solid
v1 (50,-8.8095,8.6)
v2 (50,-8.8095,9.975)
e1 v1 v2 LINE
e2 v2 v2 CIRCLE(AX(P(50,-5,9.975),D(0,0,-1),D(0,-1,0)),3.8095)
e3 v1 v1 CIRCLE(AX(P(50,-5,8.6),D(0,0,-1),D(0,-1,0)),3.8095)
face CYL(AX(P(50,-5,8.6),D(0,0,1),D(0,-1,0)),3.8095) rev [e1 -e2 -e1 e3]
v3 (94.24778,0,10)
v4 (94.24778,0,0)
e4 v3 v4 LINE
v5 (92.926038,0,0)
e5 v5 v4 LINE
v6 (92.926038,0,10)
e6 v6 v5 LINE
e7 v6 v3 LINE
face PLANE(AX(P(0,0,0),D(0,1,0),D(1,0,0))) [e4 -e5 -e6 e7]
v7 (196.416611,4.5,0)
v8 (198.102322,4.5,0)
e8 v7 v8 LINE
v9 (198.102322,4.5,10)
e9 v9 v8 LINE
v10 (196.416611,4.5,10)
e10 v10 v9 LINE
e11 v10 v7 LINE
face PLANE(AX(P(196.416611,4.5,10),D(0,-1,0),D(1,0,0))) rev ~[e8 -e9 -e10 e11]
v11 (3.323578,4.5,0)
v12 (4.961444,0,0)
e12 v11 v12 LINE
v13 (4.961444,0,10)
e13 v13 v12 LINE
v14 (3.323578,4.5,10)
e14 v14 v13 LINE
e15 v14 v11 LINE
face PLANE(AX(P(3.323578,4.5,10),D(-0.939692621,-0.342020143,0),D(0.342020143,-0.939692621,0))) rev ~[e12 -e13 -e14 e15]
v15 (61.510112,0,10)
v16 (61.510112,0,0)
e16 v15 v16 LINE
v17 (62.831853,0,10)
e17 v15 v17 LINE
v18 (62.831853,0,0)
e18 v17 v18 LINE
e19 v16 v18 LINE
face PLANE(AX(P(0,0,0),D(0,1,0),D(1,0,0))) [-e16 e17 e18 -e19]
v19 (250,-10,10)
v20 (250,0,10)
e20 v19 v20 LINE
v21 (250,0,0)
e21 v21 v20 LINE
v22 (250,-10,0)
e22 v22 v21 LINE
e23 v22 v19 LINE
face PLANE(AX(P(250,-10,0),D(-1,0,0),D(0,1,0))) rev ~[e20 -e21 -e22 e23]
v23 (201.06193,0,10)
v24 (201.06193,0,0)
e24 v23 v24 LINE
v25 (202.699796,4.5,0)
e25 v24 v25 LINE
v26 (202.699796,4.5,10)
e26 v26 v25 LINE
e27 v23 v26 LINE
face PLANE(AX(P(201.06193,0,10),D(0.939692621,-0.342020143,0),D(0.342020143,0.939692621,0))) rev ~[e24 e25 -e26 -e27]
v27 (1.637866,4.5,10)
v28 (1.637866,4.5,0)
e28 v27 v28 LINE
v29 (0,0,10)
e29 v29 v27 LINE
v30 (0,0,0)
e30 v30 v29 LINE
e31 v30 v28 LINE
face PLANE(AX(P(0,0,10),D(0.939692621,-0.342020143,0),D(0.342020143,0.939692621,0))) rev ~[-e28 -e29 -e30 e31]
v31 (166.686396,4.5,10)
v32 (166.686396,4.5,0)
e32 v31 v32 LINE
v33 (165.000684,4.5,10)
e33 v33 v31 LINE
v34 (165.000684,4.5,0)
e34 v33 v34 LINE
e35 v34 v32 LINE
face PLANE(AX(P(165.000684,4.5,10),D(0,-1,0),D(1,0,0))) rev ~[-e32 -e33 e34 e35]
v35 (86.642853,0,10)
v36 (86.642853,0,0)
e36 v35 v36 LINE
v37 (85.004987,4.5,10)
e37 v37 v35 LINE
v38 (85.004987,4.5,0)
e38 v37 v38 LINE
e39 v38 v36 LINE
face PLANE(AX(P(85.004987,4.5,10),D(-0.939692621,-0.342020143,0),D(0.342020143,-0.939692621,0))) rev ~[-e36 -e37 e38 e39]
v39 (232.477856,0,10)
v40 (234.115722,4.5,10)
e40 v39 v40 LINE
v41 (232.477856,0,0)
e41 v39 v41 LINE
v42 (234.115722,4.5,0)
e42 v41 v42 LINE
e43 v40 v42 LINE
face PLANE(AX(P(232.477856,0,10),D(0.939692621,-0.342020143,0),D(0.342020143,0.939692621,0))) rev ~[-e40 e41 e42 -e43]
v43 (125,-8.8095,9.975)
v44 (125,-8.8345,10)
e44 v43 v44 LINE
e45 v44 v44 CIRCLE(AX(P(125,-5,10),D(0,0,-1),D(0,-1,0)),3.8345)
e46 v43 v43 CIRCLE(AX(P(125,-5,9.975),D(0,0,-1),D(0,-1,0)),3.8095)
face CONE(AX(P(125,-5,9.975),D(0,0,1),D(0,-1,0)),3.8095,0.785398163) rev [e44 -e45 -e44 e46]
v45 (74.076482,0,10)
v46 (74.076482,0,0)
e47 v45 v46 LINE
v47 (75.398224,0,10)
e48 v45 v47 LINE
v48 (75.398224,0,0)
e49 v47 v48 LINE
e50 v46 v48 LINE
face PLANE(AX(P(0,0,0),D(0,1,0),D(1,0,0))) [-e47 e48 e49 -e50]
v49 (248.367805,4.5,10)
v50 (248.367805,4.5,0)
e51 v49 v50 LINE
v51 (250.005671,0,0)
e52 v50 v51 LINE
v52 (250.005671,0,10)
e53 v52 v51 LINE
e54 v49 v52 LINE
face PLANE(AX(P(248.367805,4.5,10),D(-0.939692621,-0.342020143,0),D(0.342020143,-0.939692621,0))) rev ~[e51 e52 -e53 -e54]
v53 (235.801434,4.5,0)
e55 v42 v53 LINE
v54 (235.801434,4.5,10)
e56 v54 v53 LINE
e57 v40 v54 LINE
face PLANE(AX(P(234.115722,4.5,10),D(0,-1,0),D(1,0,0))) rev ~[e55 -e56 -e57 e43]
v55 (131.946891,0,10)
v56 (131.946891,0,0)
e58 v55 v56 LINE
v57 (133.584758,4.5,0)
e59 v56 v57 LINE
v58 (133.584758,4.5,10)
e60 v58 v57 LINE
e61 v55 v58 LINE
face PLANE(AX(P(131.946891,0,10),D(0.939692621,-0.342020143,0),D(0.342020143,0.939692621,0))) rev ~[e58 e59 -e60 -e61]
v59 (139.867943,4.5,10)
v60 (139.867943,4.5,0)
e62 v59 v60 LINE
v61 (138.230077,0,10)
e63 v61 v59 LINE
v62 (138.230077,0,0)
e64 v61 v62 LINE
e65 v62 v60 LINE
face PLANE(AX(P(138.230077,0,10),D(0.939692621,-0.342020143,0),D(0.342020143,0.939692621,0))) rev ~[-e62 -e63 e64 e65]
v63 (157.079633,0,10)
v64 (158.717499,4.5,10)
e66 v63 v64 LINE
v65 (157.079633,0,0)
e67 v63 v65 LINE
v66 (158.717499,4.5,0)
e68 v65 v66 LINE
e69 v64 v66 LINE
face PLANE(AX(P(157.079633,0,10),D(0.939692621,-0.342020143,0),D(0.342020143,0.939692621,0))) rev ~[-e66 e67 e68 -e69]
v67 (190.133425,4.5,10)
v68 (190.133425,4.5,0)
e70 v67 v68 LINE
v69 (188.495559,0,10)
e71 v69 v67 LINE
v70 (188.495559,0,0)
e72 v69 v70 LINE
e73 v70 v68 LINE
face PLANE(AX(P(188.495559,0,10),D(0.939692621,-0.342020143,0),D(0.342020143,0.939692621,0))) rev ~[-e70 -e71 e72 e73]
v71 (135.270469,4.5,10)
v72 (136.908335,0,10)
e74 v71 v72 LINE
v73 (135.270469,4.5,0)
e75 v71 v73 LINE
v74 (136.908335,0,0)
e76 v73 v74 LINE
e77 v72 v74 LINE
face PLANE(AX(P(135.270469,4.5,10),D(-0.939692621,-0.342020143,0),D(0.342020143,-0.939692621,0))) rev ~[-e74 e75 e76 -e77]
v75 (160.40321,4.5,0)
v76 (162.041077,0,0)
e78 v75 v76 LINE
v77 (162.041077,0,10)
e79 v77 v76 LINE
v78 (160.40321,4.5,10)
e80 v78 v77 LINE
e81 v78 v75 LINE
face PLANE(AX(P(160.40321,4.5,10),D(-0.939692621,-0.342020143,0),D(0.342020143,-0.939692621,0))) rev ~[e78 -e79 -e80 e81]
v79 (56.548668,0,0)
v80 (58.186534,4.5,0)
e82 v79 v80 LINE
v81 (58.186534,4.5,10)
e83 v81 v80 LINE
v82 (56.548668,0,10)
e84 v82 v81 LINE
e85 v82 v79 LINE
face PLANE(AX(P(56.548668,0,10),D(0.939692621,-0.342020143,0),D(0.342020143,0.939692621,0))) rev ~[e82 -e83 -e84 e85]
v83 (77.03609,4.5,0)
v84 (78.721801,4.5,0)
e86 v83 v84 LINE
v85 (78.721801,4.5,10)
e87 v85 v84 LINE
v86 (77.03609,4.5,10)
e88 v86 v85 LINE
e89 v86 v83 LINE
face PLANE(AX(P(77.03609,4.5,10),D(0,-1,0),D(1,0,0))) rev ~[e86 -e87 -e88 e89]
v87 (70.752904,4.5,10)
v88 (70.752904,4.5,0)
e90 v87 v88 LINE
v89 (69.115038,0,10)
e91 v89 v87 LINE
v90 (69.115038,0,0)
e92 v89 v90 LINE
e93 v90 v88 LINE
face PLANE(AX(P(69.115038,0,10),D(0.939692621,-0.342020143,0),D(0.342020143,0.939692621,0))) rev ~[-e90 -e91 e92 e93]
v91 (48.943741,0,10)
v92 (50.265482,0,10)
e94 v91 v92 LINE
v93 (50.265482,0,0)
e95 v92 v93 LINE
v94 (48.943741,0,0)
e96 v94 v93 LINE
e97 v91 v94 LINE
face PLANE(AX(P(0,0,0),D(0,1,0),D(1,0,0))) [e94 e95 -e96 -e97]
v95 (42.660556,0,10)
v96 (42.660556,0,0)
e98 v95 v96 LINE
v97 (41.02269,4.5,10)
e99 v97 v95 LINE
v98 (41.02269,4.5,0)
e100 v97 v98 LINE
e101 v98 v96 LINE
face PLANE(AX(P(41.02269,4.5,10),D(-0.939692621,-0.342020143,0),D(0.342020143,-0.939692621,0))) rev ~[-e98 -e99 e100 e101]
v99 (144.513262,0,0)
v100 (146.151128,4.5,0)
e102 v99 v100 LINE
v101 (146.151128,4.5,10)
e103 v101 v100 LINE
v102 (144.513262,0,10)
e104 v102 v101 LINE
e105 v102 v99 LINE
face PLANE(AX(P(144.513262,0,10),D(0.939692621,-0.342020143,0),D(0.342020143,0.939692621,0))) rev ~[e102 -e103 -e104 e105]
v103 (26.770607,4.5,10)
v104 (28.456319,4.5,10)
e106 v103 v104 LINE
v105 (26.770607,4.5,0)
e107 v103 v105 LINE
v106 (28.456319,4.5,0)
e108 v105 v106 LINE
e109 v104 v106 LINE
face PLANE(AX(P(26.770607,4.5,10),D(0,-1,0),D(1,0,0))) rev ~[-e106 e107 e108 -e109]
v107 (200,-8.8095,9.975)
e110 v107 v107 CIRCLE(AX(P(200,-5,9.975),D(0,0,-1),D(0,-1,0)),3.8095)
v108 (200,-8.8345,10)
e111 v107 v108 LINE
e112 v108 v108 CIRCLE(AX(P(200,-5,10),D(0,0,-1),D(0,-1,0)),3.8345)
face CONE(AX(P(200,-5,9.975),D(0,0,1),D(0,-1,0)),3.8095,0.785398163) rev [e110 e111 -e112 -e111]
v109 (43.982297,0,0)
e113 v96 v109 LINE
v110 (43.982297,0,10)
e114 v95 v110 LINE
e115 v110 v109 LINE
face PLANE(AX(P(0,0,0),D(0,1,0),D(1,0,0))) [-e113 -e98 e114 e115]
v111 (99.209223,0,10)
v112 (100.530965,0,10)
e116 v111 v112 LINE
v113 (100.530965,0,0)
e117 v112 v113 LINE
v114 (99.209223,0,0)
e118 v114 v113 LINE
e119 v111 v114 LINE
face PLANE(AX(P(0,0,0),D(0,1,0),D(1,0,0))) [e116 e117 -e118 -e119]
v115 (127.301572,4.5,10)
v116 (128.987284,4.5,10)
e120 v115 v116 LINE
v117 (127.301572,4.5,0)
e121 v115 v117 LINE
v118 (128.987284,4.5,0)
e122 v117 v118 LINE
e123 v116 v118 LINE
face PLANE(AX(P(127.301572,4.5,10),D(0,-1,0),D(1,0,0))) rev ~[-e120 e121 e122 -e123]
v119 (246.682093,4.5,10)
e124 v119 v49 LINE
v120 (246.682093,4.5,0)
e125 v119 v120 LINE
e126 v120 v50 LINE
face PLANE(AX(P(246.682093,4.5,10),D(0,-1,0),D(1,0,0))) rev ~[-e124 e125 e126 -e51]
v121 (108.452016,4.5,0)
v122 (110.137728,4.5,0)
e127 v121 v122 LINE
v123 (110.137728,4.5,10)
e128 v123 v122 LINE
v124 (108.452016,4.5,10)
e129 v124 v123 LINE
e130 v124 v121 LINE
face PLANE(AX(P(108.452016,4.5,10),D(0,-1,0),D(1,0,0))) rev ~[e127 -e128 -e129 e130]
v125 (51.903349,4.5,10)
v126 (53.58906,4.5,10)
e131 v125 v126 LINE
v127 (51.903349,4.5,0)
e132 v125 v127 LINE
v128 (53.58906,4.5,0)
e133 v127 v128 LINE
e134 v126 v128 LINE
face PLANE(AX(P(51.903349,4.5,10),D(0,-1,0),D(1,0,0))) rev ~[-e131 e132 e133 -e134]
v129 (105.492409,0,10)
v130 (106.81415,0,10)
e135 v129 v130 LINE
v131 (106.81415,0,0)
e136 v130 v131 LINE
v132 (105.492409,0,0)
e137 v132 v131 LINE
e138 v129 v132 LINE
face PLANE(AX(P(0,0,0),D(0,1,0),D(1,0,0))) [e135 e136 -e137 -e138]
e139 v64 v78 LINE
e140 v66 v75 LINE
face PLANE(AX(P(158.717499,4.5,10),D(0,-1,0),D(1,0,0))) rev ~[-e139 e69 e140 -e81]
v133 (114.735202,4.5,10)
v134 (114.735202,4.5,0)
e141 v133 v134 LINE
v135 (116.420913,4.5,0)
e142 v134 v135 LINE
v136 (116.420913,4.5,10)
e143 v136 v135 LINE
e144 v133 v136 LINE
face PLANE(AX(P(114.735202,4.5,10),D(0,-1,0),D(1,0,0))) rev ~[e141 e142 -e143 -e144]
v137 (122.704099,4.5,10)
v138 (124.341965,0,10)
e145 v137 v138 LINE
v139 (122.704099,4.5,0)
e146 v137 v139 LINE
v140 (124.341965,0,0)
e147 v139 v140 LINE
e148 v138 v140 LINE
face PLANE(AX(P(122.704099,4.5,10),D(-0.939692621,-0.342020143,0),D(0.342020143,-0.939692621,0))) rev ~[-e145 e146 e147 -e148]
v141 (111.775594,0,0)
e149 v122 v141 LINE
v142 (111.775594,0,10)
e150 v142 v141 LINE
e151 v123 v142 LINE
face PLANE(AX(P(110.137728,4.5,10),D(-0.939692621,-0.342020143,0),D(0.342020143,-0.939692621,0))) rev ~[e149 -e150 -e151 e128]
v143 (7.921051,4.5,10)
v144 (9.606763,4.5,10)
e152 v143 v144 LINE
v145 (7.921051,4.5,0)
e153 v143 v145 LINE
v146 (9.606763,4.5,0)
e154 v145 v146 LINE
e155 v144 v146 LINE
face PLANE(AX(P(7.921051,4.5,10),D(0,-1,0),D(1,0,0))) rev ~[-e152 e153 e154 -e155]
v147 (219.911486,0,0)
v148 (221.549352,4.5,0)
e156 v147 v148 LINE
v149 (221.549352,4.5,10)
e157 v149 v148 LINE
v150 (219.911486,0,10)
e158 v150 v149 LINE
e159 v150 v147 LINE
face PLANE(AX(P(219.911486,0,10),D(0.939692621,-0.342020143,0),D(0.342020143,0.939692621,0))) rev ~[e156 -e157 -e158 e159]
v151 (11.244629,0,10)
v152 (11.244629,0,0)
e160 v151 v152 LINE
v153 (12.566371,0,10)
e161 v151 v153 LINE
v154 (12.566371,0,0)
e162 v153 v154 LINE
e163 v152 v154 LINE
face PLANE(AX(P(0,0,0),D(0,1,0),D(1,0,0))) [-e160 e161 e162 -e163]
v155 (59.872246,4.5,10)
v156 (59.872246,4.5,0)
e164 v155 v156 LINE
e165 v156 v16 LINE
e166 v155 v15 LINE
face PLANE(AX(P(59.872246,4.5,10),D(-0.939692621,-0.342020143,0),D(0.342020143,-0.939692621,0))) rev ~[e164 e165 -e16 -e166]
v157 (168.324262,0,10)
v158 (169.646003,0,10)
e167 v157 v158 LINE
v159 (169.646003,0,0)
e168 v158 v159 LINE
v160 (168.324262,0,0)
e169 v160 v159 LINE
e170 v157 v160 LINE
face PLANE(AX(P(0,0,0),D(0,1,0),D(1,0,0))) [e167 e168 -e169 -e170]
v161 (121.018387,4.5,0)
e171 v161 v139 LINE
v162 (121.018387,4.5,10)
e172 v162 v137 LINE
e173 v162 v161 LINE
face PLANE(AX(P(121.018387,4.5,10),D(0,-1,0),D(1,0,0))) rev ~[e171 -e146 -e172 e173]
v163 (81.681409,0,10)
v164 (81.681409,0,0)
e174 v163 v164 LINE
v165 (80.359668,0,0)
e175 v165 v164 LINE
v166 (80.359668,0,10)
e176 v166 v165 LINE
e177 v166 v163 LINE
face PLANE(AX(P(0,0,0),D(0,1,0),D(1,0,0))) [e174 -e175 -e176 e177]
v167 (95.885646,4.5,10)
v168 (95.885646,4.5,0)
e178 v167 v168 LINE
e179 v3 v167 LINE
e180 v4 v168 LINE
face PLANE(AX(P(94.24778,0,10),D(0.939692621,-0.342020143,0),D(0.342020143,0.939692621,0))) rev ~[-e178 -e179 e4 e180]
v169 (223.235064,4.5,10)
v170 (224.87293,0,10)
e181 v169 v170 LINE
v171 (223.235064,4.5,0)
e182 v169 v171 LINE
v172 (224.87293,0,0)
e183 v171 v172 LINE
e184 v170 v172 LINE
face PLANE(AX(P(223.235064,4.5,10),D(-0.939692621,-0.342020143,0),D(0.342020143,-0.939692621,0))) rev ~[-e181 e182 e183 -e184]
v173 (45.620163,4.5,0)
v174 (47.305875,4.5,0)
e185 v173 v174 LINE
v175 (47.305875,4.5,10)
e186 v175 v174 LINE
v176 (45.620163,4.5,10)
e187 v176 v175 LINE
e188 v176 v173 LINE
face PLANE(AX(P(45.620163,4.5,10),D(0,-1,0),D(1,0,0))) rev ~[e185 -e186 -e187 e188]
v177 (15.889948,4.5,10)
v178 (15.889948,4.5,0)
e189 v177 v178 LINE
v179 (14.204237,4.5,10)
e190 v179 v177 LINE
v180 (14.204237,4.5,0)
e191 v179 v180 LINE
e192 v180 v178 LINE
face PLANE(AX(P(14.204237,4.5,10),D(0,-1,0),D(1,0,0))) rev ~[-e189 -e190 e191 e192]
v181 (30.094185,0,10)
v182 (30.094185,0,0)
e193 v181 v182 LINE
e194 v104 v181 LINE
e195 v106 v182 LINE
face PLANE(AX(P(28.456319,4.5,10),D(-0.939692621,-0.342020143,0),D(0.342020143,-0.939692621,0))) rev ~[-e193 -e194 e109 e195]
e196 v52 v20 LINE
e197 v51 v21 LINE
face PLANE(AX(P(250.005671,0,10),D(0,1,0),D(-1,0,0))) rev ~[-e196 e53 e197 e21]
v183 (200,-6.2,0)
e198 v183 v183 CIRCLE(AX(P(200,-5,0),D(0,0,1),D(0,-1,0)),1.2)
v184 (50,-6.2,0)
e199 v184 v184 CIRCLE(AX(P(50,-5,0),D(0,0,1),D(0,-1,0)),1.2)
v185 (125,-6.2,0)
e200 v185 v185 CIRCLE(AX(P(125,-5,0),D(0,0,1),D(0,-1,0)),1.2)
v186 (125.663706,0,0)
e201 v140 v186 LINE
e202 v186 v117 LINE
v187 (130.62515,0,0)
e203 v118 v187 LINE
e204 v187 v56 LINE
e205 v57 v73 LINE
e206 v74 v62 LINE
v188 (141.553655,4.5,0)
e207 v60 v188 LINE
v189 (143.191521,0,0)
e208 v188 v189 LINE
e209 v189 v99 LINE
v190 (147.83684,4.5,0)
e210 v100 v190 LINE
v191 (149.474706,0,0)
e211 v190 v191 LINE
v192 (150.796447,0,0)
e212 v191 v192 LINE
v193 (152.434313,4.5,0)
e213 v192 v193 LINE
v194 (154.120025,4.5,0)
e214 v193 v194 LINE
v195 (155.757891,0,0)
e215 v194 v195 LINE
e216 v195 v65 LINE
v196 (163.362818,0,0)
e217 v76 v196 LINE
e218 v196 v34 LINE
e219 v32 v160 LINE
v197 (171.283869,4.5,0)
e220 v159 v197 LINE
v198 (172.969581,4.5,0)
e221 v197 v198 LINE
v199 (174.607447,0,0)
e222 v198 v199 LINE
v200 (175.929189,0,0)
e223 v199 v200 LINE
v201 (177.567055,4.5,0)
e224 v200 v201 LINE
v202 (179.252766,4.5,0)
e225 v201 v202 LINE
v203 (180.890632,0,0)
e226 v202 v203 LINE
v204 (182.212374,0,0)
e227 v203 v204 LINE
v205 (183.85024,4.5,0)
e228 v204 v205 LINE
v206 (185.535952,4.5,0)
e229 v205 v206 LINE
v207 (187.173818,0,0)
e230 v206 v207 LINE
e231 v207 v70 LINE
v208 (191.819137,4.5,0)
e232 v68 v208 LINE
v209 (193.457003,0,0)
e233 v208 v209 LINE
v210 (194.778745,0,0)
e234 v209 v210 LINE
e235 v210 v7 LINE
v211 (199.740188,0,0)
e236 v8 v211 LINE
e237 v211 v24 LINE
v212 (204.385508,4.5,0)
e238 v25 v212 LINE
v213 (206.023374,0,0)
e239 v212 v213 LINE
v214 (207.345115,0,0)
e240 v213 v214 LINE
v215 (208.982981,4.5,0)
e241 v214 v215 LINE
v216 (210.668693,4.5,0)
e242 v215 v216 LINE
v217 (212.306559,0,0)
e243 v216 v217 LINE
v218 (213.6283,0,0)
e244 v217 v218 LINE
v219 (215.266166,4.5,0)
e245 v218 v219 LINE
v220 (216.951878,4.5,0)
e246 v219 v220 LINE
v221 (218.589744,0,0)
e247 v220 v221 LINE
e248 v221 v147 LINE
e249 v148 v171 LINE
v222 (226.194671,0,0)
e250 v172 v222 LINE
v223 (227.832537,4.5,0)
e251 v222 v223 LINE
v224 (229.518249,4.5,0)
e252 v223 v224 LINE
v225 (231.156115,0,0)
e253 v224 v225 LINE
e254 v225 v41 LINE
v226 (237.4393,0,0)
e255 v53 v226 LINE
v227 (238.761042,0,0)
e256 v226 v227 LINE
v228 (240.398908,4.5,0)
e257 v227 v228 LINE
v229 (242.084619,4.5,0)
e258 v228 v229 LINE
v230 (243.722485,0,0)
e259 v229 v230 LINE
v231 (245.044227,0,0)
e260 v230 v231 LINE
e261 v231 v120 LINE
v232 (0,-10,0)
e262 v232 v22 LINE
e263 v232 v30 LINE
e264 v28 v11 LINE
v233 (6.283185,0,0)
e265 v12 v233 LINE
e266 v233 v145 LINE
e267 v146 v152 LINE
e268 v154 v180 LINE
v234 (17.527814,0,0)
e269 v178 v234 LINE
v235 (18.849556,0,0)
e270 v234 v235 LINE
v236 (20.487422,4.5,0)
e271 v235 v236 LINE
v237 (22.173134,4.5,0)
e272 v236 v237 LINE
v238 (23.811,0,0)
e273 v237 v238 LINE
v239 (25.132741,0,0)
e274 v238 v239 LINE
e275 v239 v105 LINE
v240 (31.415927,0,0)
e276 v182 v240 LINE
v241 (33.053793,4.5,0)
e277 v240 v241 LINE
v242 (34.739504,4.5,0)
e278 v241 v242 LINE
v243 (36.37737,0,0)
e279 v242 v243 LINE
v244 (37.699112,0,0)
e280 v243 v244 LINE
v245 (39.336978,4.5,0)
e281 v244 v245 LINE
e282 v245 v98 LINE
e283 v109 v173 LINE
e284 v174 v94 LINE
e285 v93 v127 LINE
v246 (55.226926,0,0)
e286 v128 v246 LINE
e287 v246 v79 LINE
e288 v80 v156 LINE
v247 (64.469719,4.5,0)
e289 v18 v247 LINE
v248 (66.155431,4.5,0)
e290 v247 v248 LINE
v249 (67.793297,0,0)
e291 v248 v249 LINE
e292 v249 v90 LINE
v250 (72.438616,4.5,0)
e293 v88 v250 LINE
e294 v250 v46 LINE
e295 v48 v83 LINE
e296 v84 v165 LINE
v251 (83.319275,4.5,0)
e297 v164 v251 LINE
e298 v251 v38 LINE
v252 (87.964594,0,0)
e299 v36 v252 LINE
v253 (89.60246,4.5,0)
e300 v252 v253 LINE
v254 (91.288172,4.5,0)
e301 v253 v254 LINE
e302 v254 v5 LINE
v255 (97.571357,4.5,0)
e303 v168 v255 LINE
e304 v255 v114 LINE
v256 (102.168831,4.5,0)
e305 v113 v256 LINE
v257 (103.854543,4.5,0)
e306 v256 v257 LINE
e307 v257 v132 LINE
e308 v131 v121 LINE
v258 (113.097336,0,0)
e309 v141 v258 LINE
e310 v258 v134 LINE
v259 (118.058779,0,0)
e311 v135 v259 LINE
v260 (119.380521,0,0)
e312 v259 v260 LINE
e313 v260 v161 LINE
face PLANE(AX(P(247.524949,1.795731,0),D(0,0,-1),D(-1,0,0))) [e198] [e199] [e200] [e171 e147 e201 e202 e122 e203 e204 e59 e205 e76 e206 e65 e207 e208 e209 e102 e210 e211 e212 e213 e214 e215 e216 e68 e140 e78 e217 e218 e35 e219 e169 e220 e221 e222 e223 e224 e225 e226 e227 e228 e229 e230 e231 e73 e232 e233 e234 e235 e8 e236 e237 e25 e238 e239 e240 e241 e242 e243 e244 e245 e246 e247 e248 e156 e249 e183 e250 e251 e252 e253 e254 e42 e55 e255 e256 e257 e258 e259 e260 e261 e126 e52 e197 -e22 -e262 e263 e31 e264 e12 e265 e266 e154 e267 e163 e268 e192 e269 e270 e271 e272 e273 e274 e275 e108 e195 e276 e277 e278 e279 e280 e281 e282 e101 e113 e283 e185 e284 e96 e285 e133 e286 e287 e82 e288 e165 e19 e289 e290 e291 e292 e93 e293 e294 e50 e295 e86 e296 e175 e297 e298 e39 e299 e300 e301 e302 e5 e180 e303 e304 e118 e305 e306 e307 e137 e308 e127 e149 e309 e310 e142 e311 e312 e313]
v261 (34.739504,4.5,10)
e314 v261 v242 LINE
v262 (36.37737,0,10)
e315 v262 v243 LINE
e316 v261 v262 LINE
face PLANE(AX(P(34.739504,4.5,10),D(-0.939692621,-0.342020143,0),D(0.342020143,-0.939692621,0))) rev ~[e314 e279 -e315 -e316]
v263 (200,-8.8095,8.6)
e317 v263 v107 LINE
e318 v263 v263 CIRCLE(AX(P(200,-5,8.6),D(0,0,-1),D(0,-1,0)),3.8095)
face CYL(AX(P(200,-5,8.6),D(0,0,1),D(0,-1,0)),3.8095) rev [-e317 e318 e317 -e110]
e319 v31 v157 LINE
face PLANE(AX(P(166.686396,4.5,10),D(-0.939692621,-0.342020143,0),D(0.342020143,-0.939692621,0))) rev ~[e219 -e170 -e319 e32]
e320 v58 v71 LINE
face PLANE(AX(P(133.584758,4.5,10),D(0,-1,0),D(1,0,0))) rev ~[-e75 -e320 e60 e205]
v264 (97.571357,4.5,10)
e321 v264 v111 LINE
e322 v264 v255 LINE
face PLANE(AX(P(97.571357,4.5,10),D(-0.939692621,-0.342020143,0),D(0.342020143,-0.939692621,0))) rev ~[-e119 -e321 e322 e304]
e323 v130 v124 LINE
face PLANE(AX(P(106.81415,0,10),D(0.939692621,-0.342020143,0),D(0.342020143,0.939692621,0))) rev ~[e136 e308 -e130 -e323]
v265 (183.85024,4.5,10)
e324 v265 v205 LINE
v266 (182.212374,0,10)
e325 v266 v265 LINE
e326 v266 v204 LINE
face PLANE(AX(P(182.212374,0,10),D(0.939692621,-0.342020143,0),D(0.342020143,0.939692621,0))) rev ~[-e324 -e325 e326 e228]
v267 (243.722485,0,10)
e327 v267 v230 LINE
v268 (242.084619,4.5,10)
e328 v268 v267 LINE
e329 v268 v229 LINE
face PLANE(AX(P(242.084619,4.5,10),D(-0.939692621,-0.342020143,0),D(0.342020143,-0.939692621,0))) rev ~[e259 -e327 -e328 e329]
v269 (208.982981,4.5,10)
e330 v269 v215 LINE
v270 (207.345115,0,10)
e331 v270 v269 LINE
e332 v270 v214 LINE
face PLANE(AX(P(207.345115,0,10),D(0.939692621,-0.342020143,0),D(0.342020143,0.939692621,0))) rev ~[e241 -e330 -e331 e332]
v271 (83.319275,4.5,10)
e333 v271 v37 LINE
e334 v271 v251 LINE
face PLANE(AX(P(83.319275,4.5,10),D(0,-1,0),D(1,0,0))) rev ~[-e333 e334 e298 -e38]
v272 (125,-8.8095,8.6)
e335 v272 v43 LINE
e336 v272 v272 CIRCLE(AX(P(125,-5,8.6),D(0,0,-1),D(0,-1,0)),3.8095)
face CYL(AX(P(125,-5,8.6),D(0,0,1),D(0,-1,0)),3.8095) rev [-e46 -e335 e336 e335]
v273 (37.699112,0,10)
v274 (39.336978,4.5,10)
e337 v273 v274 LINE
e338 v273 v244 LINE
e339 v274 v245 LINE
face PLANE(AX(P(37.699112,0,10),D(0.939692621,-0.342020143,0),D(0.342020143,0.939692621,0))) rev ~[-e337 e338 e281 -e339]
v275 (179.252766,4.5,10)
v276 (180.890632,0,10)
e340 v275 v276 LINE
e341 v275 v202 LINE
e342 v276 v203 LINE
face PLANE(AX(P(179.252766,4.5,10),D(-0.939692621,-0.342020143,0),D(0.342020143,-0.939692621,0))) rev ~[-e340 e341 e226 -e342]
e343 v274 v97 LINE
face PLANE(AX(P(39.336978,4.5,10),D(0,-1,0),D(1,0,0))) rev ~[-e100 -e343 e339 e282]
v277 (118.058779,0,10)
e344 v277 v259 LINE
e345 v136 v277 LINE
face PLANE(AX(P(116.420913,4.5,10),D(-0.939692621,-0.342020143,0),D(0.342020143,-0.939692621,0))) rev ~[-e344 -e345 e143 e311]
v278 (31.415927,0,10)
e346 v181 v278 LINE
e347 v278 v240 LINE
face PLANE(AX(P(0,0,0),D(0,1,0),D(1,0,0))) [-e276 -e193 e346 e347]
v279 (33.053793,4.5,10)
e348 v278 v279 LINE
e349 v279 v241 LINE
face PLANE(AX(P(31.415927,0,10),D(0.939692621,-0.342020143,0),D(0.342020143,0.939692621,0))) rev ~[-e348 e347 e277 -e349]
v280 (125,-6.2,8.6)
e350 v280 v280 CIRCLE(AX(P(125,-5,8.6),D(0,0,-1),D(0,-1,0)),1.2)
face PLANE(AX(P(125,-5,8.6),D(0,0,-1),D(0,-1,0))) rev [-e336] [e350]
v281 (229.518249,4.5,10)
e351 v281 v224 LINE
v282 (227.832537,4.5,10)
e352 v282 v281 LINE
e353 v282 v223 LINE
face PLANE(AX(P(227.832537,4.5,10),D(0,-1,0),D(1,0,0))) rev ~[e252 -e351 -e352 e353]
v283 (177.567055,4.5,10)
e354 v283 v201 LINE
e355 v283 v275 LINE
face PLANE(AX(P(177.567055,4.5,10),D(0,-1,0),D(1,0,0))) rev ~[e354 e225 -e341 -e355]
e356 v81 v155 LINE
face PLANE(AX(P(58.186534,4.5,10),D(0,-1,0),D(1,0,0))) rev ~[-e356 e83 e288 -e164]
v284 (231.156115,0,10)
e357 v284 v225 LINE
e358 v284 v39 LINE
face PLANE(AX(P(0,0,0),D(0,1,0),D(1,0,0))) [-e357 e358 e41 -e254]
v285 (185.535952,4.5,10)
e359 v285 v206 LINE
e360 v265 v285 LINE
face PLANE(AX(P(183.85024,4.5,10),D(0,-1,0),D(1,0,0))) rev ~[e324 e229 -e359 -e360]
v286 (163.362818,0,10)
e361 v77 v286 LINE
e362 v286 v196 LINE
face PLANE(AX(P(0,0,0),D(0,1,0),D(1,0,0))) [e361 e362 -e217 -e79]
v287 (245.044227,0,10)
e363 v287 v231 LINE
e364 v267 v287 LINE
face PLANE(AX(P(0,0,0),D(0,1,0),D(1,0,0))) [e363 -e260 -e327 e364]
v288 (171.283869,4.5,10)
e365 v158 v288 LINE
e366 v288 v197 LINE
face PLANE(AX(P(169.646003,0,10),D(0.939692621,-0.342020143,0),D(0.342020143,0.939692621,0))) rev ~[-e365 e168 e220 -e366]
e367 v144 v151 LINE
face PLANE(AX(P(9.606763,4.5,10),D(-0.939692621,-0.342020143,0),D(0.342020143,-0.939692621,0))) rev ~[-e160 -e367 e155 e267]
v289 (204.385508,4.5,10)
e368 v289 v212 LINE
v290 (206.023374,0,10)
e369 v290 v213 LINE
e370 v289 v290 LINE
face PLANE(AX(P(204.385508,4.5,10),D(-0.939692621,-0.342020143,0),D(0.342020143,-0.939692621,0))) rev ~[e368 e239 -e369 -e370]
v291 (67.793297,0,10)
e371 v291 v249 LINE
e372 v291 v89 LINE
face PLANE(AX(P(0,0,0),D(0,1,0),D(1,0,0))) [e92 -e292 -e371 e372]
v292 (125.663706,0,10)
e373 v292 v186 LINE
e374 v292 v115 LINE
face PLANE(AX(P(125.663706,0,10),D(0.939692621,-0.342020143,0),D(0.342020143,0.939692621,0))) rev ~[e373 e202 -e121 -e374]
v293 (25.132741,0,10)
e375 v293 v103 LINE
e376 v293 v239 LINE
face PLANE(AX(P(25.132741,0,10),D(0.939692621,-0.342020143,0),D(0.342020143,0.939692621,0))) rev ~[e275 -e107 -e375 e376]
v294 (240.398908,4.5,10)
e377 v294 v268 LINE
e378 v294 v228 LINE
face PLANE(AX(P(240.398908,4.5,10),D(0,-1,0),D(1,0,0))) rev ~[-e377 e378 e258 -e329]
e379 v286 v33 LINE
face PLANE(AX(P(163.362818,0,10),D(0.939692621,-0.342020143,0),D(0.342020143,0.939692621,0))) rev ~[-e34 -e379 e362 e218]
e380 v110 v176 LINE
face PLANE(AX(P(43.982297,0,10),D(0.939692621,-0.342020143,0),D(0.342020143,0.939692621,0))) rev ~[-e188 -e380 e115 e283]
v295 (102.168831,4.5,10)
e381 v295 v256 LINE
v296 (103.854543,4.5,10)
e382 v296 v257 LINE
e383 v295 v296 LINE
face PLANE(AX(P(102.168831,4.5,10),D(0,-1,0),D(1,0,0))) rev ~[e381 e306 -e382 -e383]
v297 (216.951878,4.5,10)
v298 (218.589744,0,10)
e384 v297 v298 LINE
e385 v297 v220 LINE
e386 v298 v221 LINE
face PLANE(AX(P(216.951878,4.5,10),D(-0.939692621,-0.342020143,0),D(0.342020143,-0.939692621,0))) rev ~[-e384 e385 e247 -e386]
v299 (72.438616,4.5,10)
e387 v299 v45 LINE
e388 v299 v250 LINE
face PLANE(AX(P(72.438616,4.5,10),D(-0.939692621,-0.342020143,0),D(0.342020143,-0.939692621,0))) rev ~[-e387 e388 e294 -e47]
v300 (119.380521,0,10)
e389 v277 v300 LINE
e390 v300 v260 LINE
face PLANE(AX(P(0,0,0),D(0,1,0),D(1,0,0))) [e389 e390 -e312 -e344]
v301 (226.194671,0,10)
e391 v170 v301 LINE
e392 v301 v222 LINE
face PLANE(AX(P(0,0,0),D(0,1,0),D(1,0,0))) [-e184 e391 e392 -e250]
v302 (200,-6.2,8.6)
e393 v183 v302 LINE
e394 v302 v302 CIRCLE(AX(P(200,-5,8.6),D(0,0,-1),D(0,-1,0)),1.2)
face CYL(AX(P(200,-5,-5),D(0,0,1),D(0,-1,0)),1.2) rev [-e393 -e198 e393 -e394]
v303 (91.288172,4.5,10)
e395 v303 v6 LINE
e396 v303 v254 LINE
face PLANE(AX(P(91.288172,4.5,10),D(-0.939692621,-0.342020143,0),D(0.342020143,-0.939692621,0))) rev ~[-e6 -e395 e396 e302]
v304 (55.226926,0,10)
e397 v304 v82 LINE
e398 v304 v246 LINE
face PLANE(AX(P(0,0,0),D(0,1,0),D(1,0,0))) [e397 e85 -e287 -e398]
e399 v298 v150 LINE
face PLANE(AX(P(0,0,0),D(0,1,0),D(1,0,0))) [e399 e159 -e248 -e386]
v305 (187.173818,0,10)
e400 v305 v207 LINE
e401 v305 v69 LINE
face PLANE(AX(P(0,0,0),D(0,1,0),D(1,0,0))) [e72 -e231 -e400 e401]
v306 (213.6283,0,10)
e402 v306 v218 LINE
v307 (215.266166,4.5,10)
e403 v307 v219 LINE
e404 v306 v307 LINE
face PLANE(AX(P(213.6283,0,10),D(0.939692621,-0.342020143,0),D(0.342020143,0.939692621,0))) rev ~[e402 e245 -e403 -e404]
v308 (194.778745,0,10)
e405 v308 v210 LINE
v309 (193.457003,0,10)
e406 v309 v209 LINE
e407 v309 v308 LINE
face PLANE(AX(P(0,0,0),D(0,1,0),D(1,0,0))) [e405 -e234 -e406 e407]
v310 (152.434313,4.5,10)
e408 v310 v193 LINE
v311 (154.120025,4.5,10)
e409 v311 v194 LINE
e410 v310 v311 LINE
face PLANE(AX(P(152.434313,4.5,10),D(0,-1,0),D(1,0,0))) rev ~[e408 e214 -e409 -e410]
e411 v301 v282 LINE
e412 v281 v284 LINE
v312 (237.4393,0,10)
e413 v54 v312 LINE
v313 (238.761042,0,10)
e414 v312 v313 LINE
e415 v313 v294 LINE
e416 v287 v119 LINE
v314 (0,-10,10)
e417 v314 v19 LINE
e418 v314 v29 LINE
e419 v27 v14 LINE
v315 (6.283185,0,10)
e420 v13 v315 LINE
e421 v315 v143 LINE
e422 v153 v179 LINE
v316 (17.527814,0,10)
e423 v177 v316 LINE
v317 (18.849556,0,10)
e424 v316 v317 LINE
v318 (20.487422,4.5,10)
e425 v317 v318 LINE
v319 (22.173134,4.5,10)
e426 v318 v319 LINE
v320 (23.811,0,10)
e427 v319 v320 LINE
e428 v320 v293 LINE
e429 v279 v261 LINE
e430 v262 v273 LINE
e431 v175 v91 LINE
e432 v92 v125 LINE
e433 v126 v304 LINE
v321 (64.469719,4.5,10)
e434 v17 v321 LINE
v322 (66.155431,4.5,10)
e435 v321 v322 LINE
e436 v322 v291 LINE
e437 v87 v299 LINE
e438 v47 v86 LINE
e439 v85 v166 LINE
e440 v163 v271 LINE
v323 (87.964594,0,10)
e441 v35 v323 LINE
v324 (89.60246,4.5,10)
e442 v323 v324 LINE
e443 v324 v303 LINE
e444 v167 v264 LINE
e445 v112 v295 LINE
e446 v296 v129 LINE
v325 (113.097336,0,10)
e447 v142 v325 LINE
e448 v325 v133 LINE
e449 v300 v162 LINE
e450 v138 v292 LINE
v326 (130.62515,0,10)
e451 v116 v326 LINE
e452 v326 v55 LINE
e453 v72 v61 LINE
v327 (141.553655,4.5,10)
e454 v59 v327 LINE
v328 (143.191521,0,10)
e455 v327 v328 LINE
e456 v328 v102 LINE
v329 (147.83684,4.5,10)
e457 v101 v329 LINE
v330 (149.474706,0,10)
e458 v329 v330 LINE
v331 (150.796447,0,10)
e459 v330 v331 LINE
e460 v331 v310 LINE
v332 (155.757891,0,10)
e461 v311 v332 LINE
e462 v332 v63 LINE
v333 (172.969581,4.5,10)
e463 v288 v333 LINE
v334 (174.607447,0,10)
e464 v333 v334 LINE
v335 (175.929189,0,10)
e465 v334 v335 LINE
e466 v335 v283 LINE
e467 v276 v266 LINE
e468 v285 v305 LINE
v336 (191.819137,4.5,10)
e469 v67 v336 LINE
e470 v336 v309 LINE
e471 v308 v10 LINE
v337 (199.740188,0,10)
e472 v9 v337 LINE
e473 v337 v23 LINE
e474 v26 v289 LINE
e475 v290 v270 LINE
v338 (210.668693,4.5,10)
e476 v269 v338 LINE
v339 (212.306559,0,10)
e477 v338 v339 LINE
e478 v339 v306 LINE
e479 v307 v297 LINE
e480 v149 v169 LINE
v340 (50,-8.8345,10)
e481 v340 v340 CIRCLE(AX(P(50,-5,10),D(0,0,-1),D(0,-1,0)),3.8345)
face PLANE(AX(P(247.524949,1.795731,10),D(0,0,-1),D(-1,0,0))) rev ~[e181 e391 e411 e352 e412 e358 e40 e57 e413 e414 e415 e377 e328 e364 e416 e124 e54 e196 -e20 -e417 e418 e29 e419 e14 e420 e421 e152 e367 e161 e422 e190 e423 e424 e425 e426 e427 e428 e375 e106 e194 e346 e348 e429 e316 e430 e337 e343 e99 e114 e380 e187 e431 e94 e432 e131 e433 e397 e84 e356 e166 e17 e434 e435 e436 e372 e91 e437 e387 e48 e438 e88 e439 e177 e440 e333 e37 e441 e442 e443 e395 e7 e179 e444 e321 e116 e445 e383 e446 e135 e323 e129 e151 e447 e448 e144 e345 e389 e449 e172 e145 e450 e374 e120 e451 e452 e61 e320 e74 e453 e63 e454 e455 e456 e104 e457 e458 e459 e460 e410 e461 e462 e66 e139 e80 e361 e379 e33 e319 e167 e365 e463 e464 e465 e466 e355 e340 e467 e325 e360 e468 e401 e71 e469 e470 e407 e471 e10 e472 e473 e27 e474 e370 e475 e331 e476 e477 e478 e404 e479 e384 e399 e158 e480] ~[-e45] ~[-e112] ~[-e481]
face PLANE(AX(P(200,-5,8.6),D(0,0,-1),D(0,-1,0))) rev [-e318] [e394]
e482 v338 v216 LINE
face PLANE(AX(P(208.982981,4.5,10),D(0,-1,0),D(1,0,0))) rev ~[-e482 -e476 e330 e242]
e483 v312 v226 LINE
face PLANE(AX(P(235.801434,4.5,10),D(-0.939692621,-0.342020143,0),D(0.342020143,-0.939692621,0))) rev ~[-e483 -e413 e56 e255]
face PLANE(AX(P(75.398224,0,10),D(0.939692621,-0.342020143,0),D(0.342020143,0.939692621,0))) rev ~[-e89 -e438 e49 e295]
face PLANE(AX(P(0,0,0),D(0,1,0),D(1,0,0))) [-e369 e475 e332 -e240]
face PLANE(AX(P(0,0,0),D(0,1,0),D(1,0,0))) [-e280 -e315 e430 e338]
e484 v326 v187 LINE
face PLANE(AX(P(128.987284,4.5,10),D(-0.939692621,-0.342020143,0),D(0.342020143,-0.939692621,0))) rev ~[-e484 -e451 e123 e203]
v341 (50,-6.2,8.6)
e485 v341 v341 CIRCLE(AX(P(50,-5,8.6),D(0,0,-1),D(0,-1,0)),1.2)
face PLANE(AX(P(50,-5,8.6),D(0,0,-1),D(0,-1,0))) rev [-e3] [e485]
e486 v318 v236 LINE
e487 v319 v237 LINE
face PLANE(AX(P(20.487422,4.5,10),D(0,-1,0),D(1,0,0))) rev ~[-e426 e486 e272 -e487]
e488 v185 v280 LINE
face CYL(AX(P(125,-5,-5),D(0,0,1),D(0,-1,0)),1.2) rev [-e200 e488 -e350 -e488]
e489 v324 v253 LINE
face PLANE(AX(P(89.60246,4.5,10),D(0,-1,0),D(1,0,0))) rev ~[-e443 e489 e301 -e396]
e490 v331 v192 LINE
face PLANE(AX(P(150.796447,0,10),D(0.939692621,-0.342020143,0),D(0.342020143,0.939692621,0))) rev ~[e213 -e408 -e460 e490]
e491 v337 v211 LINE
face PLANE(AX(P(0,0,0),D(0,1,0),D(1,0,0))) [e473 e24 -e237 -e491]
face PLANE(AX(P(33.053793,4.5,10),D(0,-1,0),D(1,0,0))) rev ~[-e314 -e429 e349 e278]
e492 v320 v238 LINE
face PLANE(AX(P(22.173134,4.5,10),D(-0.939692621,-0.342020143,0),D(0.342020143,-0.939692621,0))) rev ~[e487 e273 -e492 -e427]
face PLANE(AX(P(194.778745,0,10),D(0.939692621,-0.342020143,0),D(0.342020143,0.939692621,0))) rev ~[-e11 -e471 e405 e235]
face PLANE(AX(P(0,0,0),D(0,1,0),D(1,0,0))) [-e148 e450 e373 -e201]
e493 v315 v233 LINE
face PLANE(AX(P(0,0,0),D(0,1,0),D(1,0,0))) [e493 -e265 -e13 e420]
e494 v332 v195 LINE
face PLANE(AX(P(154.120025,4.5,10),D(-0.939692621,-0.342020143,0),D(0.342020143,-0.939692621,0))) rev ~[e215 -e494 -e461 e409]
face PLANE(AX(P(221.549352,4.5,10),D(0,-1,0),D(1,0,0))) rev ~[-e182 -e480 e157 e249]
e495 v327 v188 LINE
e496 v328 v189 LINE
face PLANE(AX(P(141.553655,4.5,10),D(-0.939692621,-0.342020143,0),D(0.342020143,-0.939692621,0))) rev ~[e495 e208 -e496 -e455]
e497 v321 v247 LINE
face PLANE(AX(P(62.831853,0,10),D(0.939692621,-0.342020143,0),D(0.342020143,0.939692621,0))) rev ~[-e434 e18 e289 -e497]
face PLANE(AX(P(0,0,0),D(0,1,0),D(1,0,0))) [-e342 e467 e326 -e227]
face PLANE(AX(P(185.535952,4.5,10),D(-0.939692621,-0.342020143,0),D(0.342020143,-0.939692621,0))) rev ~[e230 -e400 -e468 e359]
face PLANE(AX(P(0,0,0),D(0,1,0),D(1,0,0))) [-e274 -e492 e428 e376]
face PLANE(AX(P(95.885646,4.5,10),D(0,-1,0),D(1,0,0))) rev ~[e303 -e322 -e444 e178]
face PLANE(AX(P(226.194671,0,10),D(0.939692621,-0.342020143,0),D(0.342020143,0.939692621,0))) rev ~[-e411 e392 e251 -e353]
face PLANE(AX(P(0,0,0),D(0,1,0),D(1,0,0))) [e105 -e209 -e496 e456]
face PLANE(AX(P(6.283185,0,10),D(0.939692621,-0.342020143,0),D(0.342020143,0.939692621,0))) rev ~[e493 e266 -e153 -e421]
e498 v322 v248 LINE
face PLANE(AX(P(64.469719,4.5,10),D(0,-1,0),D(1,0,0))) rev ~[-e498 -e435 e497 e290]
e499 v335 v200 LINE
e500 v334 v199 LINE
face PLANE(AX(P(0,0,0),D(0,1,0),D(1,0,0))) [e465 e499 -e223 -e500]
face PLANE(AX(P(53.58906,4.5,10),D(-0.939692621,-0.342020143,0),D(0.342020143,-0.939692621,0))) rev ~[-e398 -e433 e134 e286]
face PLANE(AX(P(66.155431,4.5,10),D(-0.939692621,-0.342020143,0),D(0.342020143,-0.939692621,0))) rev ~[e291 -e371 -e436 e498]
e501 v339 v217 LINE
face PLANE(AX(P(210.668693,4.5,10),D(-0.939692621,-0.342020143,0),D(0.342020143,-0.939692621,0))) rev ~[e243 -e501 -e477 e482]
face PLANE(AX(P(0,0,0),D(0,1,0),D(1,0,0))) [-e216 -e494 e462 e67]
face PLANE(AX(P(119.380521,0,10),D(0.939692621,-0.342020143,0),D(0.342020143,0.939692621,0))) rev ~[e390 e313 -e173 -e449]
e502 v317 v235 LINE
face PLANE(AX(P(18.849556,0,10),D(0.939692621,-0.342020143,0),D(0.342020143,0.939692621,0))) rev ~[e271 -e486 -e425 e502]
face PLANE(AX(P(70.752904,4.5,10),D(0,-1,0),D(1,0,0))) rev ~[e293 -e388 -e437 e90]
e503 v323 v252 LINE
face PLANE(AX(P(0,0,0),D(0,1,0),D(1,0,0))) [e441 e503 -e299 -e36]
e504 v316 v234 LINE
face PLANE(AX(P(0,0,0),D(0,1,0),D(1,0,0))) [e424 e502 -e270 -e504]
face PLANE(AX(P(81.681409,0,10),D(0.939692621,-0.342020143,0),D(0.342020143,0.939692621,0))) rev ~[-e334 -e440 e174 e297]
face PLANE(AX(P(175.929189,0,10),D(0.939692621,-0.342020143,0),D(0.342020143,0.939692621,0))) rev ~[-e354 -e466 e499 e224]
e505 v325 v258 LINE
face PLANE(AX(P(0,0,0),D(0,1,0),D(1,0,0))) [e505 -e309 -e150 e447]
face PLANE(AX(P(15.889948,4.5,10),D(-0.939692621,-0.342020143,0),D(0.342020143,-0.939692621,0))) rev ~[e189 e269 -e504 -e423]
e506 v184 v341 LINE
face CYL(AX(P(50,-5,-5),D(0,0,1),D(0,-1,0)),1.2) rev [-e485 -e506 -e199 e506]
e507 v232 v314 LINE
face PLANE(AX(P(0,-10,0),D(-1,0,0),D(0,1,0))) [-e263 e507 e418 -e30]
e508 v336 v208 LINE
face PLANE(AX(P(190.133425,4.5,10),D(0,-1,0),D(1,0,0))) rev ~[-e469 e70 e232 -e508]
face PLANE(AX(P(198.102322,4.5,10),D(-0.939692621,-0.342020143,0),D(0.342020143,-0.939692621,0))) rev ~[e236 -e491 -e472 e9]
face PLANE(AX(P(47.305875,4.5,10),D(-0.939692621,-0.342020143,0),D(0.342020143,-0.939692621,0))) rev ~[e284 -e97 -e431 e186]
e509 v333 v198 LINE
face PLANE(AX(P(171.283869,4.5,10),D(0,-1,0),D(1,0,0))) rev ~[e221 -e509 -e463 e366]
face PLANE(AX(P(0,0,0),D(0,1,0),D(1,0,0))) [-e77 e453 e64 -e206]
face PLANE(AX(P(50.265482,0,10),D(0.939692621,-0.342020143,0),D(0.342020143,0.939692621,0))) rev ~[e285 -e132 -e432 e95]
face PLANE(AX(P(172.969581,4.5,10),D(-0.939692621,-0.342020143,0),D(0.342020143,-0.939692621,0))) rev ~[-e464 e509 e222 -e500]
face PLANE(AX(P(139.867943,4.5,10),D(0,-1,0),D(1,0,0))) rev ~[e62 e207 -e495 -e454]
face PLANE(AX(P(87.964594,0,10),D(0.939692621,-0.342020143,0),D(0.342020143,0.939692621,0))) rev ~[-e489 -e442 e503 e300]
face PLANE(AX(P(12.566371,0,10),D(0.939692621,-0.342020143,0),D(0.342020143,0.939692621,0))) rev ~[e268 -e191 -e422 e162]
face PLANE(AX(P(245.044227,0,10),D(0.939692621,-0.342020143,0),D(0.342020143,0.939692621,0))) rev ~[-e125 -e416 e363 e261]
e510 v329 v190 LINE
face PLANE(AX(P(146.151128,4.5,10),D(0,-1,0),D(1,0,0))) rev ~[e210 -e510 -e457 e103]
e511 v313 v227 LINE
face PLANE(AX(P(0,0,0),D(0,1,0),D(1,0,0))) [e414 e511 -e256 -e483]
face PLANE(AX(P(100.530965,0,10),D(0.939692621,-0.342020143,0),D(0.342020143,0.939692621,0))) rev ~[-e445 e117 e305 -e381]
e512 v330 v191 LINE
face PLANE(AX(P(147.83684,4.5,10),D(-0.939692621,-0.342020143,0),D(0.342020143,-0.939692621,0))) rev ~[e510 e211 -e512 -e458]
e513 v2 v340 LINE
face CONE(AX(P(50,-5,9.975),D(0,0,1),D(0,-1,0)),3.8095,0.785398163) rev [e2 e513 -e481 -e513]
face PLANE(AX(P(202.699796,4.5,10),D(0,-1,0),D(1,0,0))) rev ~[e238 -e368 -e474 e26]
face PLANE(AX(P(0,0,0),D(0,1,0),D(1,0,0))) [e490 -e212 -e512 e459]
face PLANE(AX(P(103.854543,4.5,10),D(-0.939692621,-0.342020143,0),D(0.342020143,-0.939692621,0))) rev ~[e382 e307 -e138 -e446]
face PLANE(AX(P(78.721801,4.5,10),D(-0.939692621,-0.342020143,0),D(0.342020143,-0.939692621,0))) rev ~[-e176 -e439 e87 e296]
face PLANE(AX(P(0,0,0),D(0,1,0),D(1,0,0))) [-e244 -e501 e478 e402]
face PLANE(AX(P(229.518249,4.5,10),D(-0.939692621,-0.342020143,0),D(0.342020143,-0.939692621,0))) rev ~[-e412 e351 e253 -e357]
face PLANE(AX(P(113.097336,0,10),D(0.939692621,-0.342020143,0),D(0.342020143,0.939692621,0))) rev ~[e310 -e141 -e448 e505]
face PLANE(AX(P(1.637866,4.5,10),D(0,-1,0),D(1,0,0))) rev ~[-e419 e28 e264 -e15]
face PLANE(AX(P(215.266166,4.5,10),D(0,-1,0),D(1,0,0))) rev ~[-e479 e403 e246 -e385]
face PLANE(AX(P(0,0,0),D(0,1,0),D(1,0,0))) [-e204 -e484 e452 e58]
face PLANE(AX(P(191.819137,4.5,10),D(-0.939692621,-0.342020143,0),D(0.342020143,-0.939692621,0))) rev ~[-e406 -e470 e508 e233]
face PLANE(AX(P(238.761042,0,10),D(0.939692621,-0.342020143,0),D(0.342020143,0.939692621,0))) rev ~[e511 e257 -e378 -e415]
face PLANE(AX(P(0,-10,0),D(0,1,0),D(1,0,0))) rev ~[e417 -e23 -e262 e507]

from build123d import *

# Parameters (mm, degrees)
SKETCH1_W                              = 250
SKETCH1_H                              = 10
EXTRUDE1_DEPTH                         = 10
EXTRUDE2_DEPTH                         = 10
LPATTERN1_COUNT                        = 40
LPATTERN1_PITCH                        = 6.283185307
CBORE_FOR_M2_HEX_CAP_SCREW1_AT_2_COUNT = 2
CBORE_FOR_M2_HEX_CAP_SCREW1_AT_2_PITCH = 75
CBORE_FOR_M2_HEX_CAP_SCREW1_AT_3_COUNT = 2
CBORE_FOR_M2_HEX_CAP_SCREW1_AT_3_PITCH = 150


with BuildPart() as part:
    # Sketch1 → Extrude1 (new body)
    with BuildSketch(Plane.XY):
        with Locations((125, -5)):
            Rectangle(SKETCH1_W, SKETCH1_H)
    extrude(amount=EXTRUDE1_DEPTH)

    # Sketch2 → Extrude2 (add)
    with BuildSketch(Plane.XY.offset(10)):
        Polygon((0, 0), (1.637866054, 4.5), (3.323577771, 4.5), (4.961443825, 0), align=None)
    extrude2 = extrude(amount=-EXTRUDE2_DEPTH)

    # LPattern1: Extrude2 ×40
    with Locations(*[(i * LPATTERN1_PITCH, 0, 0) for i in range(1, LPATTERN1_COUNT)]):
        add(extrude2)

    # Sketch13 → CBORE for M2 Hex Cap Screw1 (revolve, cut)
    with BuildSketch(Plane(origin=(50, -5, 10), x_dir=(0, -1, 0), z_dir=(1, 0, 0))):
        Polygon((0, 0), (0, 15.721032743), (1.2, 15), (1.2, 1.4), (3.8095, 1.4), (3.8095, 0.025), (3.8345, 0), align=None)
    cbore_for_m2_hex_cap_screw1 = revolve(axis=Axis((50, -5, 16.35), (0, 0, -1)), mode=Mode.SUBTRACT)

    # CBORE for M2 Hex Cap Screw1 at 2: CBORE for M2 Hex Cap Screw1 ×2
    with Locations(*[(i * CBORE_FOR_M2_HEX_CAP_SCREW1_AT_2_PITCH, 0, 0) for i in range(1, CBORE_FOR_M2_HEX_CAP_SCREW1_AT_2_COUNT)]):
        add(cbore_for_m2_hex_cap_screw1, mode=Mode.SUBTRACT)

    # CBORE for M2 Hex Cap Screw1 at 3: CBORE for M2 Hex Cap Screw1 ×2
    with Locations(*[(i * CBORE_FOR_M2_HEX_CAP_SCREW1_AT_3_PITCH, 0, 0) for i in range(1, CBORE_FOR_M2_HEX_CAP_SCREW1_AT_3_COUNT)]):
        add(cbore_for_m2_hex_cap_screw1, mode=Mode.SUBTRACT)


solid = part.part
